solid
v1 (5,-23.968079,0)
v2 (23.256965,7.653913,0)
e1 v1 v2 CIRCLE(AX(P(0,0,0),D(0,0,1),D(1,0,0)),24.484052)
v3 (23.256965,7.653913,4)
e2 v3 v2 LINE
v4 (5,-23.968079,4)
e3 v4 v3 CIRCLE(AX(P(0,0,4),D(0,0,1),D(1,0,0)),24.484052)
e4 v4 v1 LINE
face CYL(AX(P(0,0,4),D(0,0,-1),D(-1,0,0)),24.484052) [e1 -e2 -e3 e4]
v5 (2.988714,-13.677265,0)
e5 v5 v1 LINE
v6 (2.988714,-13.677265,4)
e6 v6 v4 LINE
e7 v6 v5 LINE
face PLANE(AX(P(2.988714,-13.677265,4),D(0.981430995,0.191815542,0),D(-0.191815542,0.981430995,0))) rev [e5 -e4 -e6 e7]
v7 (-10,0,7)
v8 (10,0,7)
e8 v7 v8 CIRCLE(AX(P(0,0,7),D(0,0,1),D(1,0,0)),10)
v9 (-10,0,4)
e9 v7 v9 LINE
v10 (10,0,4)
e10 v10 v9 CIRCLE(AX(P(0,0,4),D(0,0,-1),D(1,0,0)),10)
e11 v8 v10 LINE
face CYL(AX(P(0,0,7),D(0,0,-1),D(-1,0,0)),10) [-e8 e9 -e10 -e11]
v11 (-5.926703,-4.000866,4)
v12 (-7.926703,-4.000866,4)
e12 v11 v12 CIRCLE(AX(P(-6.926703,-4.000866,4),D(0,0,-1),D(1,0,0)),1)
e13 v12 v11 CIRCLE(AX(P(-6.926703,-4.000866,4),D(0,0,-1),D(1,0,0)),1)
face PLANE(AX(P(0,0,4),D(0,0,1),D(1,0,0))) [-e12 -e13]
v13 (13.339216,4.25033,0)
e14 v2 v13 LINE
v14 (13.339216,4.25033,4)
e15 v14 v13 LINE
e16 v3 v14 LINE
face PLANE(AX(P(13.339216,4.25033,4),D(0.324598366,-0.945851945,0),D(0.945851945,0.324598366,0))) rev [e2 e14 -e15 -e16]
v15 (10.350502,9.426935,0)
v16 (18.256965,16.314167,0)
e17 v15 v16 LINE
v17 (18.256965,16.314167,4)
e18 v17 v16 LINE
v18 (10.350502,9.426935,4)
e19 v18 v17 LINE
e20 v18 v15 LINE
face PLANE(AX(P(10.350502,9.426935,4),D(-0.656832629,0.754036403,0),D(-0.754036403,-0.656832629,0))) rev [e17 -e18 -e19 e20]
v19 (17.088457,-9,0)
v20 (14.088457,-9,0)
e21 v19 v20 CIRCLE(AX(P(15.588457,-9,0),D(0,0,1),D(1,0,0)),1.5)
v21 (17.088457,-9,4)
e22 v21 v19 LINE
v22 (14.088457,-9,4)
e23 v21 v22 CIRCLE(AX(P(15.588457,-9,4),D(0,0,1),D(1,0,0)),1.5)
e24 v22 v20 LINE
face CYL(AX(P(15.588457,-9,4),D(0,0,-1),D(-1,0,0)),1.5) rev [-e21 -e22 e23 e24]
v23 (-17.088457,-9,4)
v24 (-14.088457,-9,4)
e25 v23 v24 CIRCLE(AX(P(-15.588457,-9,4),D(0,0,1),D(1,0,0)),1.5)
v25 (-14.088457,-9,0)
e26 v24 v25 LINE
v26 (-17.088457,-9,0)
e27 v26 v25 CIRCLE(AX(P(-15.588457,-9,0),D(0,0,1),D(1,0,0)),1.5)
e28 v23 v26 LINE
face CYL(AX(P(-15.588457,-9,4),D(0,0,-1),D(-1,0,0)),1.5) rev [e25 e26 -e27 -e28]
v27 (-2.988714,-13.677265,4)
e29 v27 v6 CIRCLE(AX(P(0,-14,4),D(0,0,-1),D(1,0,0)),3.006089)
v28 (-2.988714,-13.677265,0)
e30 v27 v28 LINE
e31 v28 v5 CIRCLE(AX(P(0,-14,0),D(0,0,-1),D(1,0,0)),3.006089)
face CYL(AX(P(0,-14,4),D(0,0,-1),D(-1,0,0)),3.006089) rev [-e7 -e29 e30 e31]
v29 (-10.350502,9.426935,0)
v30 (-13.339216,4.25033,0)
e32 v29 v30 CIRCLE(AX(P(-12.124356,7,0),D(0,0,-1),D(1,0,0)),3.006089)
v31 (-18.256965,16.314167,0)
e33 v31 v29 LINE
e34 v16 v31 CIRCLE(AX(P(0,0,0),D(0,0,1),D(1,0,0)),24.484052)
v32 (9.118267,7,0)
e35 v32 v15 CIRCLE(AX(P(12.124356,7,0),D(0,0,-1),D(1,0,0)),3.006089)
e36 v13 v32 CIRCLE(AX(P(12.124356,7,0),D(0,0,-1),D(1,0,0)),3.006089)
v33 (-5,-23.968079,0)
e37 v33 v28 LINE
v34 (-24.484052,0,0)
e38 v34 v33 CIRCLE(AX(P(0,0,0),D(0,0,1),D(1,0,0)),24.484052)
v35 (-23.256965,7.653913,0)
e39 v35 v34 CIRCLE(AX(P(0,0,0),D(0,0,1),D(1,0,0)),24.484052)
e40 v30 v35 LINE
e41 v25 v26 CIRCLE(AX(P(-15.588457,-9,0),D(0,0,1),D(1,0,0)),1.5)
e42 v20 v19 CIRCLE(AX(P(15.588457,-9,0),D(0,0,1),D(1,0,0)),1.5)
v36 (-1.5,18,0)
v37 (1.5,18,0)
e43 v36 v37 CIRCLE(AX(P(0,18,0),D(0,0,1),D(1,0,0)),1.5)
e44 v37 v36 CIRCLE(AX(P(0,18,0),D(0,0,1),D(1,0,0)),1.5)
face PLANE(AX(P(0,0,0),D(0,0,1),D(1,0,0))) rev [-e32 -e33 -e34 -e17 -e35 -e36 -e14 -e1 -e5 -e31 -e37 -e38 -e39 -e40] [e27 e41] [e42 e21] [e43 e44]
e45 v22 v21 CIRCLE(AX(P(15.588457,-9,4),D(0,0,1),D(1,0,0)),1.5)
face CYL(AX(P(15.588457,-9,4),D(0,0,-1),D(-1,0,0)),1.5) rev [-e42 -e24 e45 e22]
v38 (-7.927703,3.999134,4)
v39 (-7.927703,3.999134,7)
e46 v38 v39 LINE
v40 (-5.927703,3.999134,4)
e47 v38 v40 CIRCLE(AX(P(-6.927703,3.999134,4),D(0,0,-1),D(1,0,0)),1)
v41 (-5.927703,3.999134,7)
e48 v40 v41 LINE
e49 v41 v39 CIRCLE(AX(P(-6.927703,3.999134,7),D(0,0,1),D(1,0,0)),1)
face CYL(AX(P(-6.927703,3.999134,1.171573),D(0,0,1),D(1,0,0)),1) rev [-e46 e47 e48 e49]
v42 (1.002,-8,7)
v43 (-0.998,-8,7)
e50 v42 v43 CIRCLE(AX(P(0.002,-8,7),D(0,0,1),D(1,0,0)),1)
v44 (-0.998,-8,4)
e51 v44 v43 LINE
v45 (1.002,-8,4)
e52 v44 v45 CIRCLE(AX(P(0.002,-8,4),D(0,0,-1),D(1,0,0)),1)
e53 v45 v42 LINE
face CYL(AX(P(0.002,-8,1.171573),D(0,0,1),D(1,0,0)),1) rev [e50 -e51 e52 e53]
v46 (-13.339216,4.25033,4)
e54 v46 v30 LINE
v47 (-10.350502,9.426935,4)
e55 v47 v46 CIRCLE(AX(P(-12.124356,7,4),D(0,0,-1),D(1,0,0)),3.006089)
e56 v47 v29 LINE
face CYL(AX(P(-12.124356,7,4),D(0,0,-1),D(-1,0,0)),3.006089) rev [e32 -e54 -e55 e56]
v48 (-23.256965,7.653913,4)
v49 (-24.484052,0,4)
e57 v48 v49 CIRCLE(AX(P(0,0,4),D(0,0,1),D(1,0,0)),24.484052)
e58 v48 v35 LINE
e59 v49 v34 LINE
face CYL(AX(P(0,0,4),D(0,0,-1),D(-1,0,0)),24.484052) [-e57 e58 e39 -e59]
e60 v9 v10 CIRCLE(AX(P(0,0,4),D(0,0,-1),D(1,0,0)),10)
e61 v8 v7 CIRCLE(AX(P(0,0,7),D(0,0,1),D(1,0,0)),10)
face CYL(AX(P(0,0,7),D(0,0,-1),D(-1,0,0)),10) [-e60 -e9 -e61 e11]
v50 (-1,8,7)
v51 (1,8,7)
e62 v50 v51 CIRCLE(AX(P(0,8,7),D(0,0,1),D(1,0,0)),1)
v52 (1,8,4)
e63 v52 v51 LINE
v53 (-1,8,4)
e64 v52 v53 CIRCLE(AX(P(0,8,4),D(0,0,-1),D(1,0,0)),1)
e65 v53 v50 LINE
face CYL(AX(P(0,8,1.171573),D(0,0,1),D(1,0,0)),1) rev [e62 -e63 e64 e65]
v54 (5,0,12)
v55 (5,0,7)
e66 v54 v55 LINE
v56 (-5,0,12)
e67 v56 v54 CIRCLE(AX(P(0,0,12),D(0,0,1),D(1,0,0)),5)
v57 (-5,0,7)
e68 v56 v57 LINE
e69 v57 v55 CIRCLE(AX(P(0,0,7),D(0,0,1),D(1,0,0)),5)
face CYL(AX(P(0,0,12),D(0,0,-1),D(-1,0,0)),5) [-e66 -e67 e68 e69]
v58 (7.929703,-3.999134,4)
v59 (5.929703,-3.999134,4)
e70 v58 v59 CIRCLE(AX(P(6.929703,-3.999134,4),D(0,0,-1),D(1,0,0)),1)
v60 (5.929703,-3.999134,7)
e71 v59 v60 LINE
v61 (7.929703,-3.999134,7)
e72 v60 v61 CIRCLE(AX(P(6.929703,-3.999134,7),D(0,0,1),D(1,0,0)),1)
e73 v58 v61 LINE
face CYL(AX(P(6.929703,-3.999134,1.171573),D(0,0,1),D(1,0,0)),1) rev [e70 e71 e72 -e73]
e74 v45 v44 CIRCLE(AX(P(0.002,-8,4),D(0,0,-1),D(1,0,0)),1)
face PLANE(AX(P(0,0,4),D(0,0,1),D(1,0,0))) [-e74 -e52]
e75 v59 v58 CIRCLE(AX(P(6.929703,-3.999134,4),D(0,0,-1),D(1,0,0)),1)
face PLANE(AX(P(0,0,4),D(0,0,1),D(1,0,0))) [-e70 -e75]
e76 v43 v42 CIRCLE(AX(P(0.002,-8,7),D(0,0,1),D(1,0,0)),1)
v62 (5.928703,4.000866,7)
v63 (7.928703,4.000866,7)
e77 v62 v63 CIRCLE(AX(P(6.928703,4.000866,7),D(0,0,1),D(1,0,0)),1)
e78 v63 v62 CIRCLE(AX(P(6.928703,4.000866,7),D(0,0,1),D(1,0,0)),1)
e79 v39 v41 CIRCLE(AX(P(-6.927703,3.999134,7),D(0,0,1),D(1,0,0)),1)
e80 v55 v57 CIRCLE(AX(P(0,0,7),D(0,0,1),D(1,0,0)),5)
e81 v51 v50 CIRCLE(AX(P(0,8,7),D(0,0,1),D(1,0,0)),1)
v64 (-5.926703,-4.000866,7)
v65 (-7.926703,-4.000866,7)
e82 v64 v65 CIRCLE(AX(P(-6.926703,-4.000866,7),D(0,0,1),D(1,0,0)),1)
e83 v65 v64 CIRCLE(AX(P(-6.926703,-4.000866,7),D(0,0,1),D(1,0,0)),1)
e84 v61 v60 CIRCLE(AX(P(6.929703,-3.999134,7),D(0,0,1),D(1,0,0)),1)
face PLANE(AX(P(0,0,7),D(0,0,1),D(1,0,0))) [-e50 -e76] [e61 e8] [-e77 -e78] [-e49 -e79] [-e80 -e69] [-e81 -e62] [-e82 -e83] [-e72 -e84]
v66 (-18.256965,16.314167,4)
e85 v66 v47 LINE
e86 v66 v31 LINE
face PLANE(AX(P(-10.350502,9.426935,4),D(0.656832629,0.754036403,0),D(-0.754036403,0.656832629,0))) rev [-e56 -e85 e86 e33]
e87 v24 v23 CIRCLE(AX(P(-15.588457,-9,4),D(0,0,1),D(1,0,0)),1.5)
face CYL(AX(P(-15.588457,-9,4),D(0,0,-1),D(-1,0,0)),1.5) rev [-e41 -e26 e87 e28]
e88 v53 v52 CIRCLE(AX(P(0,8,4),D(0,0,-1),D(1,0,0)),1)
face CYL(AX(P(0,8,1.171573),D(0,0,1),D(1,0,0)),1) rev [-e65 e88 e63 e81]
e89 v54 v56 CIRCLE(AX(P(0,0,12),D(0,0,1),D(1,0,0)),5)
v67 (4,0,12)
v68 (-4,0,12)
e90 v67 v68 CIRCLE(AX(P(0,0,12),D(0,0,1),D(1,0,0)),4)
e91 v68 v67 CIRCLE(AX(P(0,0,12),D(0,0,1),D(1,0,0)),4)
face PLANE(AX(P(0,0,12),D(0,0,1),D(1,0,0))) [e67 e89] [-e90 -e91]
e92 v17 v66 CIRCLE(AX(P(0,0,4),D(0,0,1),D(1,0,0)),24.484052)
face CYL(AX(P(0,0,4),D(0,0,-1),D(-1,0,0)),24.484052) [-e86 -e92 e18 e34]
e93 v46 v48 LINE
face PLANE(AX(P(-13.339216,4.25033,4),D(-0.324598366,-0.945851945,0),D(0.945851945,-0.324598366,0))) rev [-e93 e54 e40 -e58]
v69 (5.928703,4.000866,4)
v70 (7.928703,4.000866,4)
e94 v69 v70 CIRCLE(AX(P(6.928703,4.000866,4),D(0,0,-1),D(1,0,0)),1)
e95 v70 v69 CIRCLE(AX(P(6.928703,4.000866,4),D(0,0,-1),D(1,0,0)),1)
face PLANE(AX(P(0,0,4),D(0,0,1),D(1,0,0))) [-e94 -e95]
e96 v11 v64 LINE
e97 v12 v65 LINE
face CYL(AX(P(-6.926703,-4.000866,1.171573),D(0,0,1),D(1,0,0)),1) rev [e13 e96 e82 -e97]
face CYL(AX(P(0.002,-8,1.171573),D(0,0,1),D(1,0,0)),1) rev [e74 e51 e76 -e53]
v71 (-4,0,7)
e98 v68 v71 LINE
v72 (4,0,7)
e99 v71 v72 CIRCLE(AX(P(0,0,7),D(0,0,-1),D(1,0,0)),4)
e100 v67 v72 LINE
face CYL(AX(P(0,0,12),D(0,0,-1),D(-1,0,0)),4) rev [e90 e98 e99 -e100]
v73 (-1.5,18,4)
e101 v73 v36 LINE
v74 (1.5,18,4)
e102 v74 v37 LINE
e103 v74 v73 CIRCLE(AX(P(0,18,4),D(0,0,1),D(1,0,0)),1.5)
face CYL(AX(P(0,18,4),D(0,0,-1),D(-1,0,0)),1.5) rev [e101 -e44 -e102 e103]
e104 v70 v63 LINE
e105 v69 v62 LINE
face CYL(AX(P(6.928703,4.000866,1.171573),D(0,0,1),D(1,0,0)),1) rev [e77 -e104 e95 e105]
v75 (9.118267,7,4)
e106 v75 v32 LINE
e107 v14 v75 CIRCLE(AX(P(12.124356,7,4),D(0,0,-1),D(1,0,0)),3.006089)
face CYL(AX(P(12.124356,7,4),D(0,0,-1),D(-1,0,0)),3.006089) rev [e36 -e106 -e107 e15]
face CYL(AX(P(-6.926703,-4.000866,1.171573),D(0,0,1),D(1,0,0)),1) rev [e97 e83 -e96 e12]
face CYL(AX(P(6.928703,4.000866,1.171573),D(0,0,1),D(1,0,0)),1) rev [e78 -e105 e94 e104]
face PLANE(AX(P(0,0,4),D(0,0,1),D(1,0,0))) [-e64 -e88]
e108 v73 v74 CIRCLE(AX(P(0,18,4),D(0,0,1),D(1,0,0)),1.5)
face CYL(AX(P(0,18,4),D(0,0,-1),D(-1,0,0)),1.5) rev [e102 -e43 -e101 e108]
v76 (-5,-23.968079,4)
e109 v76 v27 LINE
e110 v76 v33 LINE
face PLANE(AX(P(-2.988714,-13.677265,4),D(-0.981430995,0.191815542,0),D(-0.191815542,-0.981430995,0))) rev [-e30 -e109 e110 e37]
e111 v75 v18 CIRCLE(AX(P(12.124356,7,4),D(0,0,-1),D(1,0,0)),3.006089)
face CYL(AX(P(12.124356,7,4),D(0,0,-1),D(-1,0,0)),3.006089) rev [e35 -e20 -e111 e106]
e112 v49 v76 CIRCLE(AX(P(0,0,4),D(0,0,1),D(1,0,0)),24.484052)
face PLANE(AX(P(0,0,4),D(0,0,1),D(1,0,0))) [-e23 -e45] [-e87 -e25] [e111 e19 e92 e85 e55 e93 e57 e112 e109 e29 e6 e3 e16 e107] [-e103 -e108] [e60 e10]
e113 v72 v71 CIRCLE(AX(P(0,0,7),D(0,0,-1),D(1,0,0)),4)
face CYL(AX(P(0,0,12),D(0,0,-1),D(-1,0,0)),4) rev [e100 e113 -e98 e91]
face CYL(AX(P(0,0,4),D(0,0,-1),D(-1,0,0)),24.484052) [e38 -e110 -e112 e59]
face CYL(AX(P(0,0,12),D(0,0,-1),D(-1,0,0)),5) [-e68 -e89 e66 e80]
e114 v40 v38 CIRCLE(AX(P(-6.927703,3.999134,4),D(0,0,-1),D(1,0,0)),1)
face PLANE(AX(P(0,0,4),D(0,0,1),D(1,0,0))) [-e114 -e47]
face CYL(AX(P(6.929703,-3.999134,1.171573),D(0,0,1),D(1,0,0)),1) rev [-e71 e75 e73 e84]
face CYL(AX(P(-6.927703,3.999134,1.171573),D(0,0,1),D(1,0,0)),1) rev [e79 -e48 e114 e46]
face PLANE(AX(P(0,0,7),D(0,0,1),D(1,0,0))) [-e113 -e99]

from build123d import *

# Parameters (mm, degrees)
FLANGE_PLATE_4MM_DEPTH   = 4
OUTER_HOLES_SKETCH_R     = 1.5
OUTER_HOLES_3X_DEPTH     = 35.855955648
HUB_SKETCH_R             = 10
RAISED_HUB_DEPTH         = 7
HUB_HOLES_SKETCH_R       = 1
HUB_HOLES_6X_DEPTH       = 3
CENTRE_SLEEVE_SKETCH_R   = 5
CENTRE_SLEEVE_SKETCH_R_2 = 4
CENTRE_SLEEVE_DEPTH      = 5


with BuildPart() as part:
    # Flange Plate Sketch → Flange Plate 4mm (new body)
    with BuildSketch(Plane.XY):
        with BuildLine():
            Line((-2.988714381, -13.67726531), (-5, -23.968079232))
            ThreePointArc((-5, -23.968079232), (-21.203811369, -12.242026202), (-23.256965495, 7.653912597))
            Line((-23.256965495, 7.653912597), (-13.339216403, 4.250330076))
            ThreePointArc((-13.339216403, 4.250330076), (-9.521006176, 5.496955479), (-10.350502022, 9.426935234))
            Line((-10.350502022, 9.426935234), (-18.256965495, 16.314166635))
            ThreePointArc((-18.256965495, 16.314166635), (0, 24.484052403), (18.256965495, 16.314166635))
            Line((18.256965495, 16.314166635), (10.350502022, 9.426935234))
            ThreePointArc((10.350502022, 9.426935234), (9.521006176, 5.496955479), (13.339216403, 4.250330076))
            Line((13.339216403, 4.250330076), (23.256965495, 7.653912597))
            ThreePointArc((23.256965495, 7.653912597), (21.203811369, -12.242026202), (5, -23.968079232))
            Line((5, -23.968079232), (2.988714381, -13.67726531))
            ThreePointArc((2.988714381, -13.67726531), (0, -10.993910957), (-2.988714381, -13.67726531))
        make_face()
    extrude(amount=FLANGE_PLATE_4MM_DEPTH)

    # Outer Holes Sketch → Outer Holes 3x (cut, through all)
    with BuildSketch(Plane.XY):
        with Locations((0, 18)):
            Circle(OUTER_HOLES_SKETCH_R)
        with Locations((15.588457268, -9)):
            Circle(OUTER_HOLES_SKETCH_R)
        with Locations((-15.588457268, -9)):
            Circle(OUTER_HOLES_SKETCH_R)
    extrude(amount=OUTER_HOLES_3X_DEPTH, mode=Mode.SUBTRACT)

    # Hub Sketch → Raised Hub (add)
    with BuildSketch(Plane.XY):
        Circle(HUB_SKETCH_R)
    extrude(amount=RAISED_HUB_DEPTH)

    # Hub Holes Sketch → Hub Holes 6x (cut)
    with BuildSketch(Plane.XY.offset(7)):
        with Locations((0, 8)):
            Circle(HUB_HOLES_SKETCH_R)
        with Locations((6.92870323, 4.000866025)):
            Circle(HUB_HOLES_SKETCH_R)
        with Locations((6.92970323, -3.999133975)):
            Circle(HUB_HOLES_SKETCH_R)
        with Locations((0.002, -8)):
            Circle(HUB_HOLES_SKETCH_R)
        with Locations((-6.92670323, -4.000866025)):
            Circle(HUB_HOLES_SKETCH_R)
        with Locations((-6.92770323, 3.999133975)):
            Circle(HUB_HOLES_SKETCH_R)
    extrude(amount=-HUB_HOLES_6X_DEPTH, mode=Mode.SUBTRACT)

    # Centre Sleeve Sketch → Centre Sleeve (add)
    with BuildSketch(Plane.XY.offset(7)):
        Circle(CENTRE_SLEEVE_SKETCH_R)
        Circle(CENTRE_SLEEVE_SKETCH_R_2, mode=Mode.SUBTRACT)
    extrude(amount=CENTRE_SLEEVE_DEPTH)


solid = part.part
